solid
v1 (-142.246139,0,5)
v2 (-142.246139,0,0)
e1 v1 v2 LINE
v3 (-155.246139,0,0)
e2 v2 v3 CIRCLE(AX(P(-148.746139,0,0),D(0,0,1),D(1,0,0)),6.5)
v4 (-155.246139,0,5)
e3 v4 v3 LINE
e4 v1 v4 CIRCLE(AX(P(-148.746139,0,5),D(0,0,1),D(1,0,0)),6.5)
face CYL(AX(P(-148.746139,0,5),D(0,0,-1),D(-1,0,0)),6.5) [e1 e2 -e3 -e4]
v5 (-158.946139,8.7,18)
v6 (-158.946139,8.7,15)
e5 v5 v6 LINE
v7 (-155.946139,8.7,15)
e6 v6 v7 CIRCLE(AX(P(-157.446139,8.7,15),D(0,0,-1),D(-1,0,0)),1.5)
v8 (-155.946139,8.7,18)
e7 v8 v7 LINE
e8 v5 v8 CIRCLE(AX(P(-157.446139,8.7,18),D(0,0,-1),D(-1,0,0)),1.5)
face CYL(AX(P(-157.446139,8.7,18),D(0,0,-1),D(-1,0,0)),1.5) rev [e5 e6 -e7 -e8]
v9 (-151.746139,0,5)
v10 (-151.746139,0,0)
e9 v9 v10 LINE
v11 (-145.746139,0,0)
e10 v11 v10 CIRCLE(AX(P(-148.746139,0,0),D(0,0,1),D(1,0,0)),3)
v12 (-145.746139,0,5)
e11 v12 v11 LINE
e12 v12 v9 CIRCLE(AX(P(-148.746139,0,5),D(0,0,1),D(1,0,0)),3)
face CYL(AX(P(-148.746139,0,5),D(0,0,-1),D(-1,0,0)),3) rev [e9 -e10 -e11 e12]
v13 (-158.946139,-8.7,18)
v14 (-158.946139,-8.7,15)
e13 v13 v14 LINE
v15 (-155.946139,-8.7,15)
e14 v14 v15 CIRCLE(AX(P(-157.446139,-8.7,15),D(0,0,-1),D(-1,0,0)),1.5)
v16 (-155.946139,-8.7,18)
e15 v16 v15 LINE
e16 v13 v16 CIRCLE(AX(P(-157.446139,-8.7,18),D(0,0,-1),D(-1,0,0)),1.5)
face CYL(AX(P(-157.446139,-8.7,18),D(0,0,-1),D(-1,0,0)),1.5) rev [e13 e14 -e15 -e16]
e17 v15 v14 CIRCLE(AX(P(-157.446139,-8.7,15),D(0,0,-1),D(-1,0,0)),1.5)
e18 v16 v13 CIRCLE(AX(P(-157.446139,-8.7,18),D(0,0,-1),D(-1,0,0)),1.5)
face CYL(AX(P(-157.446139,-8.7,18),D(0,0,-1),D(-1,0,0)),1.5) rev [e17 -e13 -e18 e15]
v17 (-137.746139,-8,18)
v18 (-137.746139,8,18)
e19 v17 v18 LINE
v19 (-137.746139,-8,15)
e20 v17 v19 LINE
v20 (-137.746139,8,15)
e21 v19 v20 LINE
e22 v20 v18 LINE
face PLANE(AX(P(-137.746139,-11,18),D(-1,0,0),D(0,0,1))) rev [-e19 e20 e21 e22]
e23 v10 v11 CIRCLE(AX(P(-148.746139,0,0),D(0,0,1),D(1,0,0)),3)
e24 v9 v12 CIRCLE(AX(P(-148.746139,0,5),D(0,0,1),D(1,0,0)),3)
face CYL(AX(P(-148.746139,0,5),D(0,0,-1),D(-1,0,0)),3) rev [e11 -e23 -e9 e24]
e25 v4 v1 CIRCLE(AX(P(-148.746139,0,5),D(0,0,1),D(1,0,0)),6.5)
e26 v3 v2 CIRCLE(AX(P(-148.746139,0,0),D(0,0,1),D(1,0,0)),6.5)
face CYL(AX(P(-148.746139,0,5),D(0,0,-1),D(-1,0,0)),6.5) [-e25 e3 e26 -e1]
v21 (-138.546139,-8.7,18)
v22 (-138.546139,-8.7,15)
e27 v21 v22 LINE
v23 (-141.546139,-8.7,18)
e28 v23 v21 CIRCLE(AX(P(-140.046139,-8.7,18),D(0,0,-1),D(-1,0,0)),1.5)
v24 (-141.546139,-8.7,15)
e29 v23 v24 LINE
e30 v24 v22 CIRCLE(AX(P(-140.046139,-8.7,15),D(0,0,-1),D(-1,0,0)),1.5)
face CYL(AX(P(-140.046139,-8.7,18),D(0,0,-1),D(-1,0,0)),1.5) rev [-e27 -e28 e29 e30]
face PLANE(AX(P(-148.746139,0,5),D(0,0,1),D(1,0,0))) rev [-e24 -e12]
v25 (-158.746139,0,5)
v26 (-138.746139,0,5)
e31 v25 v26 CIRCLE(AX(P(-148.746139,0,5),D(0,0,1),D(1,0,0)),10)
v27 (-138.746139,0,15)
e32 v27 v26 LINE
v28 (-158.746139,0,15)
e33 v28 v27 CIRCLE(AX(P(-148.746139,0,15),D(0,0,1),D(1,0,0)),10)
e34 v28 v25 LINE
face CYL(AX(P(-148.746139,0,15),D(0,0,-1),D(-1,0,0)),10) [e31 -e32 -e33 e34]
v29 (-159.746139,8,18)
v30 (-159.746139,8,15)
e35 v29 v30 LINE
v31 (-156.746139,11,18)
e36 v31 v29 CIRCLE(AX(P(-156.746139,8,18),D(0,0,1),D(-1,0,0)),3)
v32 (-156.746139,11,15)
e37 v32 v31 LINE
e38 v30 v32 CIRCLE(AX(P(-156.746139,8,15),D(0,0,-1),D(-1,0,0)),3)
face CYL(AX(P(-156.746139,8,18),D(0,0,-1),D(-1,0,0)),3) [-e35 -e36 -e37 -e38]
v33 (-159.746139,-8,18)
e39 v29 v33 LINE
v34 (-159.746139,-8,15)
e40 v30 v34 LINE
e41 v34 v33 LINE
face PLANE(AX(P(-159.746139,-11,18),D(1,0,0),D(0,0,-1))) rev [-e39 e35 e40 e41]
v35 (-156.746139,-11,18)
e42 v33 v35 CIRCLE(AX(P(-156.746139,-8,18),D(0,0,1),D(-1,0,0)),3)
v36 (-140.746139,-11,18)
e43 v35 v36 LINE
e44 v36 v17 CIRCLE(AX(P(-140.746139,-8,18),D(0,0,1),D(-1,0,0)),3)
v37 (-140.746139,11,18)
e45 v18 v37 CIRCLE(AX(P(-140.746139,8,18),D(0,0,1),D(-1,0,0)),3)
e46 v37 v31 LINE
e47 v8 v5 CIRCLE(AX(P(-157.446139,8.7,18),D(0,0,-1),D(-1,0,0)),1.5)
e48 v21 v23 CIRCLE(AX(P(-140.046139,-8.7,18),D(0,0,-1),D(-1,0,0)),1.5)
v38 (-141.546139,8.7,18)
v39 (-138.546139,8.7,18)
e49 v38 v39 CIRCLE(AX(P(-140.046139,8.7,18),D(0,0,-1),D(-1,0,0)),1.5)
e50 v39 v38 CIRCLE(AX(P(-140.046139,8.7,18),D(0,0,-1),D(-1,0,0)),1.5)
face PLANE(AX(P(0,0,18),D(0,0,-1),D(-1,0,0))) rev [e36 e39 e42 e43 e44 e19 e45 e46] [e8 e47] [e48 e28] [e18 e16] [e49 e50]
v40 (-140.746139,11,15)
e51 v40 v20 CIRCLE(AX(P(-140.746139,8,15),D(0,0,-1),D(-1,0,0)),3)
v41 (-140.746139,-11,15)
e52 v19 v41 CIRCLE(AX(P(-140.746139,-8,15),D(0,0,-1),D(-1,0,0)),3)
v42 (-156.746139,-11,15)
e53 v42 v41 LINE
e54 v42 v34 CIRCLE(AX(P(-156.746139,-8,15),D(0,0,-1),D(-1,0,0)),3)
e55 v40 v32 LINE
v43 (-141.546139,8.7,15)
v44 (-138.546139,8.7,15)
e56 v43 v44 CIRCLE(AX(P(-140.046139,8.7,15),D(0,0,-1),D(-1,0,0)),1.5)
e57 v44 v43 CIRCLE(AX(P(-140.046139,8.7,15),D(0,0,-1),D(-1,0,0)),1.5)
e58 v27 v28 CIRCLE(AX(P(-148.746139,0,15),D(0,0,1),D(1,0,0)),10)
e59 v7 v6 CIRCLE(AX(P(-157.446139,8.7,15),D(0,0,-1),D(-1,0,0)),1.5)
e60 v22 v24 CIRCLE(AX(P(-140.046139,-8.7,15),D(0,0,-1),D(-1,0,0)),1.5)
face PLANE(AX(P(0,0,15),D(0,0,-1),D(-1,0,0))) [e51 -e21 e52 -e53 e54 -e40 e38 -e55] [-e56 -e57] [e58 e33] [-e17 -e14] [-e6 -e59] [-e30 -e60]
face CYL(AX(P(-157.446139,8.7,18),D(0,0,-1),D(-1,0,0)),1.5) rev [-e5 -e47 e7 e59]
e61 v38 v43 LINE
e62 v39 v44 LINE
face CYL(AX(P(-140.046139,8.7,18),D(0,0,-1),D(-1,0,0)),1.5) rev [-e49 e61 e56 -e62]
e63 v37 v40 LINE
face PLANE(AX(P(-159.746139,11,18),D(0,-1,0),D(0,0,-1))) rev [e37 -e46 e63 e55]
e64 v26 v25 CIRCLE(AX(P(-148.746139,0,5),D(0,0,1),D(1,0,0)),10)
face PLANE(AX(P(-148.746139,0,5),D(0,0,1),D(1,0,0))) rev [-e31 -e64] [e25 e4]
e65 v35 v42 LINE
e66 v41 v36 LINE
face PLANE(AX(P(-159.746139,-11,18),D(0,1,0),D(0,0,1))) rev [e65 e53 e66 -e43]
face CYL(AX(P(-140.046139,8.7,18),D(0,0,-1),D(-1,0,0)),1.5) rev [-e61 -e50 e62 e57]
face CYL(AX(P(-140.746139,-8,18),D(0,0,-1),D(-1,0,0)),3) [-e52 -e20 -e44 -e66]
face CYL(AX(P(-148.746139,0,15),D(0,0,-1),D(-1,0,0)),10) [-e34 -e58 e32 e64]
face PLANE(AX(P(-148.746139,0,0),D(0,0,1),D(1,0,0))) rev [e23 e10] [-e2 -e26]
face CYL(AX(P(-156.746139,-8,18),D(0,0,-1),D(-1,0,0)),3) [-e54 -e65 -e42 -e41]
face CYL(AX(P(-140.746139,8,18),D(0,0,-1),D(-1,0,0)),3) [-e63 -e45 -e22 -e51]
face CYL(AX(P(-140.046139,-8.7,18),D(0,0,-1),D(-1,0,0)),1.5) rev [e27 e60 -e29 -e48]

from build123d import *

# Parameters (mm, degrees)
SKETCH1_R           = 6.5
SKETCH1_R_2         = 3
BOSS_EXTRUDE1_DEPTH = 5
SKETCH2_R           = 10
BOSS_EXTRUDE2_DEPTH = 10
SKETCH3_W           = 22
SKETCH3_H           = 22
BOSS_EXTRUDE3_DEPTH = 3
FILLET1_R           = 3
SKETCH4_R           = 1.5
CUT_EXTRUDE1_DEPTH  = 3


with BuildPart() as part:
    # Sketch1 → Boss-Extrude1 (new body)
    with BuildSketch(Plane.XY):
        with Locations((-148.746139417, 0)):
            Circle(SKETCH1_R)
        with Locations((-148.746139417, 0)):
            Circle(SKETCH1_R_2, mode=Mode.SUBTRACT)
    extrude(amount=BOSS_EXTRUDE1_DEPTH)

    # Sketch2 → Boss-Extrude2 (add)
    with BuildSketch(Plane.XY.offset(5)):
        with Locations((-148.746139417, 0)):
            Circle(SKETCH2_R)
    extrude(amount=BOSS_EXTRUDE2_DEPTH)

    # Sketch3 → Boss-Extrude3 (add)
    with BuildSketch(Plane.XY.offset(15)):
        with Locations((-148.746139417, 0)):
            Rectangle(SKETCH3_W, SKETCH3_H)
    extrude(amount=BOSS_EXTRUDE3_DEPTH)

    # Fillet1
    fillet1_edges = [part.edges().sort_by_distance(p)[0] for p in [
        (-137.746139417, -11, 16.5),
        (-137.746139417, 11, 16.5),
        (-159.746139417, 11, 16.5),
        (-159.746139417, -11, 16.5),
    ]]
    fillet(fillet1_edges, radius=FILLET1_R)

    # Sketch4 → Cut-Extrude1 (cut)
    with BuildSketch(Plane(origin=(0, 0, 15), x_dir=(-1, 0, 0), z_dir=(0, 0, -1))):
        with Locations((157.446139417, 8.7)):
            Circle(SKETCH4_R)
        with Locations((157.446139417, -8.7)):
            Circle(SKETCH4_R)
        with Locations((140.046139417, -8.7)):
            Circle(SKETCH4_R)
        with Locations((140.046139417, 8.7)):
            Circle(SKETCH4_R)
    extrude(amount=-CUT_EXTRUDE1_DEPTH, mode=Mode.SUBTRACT)


solid = part.part
